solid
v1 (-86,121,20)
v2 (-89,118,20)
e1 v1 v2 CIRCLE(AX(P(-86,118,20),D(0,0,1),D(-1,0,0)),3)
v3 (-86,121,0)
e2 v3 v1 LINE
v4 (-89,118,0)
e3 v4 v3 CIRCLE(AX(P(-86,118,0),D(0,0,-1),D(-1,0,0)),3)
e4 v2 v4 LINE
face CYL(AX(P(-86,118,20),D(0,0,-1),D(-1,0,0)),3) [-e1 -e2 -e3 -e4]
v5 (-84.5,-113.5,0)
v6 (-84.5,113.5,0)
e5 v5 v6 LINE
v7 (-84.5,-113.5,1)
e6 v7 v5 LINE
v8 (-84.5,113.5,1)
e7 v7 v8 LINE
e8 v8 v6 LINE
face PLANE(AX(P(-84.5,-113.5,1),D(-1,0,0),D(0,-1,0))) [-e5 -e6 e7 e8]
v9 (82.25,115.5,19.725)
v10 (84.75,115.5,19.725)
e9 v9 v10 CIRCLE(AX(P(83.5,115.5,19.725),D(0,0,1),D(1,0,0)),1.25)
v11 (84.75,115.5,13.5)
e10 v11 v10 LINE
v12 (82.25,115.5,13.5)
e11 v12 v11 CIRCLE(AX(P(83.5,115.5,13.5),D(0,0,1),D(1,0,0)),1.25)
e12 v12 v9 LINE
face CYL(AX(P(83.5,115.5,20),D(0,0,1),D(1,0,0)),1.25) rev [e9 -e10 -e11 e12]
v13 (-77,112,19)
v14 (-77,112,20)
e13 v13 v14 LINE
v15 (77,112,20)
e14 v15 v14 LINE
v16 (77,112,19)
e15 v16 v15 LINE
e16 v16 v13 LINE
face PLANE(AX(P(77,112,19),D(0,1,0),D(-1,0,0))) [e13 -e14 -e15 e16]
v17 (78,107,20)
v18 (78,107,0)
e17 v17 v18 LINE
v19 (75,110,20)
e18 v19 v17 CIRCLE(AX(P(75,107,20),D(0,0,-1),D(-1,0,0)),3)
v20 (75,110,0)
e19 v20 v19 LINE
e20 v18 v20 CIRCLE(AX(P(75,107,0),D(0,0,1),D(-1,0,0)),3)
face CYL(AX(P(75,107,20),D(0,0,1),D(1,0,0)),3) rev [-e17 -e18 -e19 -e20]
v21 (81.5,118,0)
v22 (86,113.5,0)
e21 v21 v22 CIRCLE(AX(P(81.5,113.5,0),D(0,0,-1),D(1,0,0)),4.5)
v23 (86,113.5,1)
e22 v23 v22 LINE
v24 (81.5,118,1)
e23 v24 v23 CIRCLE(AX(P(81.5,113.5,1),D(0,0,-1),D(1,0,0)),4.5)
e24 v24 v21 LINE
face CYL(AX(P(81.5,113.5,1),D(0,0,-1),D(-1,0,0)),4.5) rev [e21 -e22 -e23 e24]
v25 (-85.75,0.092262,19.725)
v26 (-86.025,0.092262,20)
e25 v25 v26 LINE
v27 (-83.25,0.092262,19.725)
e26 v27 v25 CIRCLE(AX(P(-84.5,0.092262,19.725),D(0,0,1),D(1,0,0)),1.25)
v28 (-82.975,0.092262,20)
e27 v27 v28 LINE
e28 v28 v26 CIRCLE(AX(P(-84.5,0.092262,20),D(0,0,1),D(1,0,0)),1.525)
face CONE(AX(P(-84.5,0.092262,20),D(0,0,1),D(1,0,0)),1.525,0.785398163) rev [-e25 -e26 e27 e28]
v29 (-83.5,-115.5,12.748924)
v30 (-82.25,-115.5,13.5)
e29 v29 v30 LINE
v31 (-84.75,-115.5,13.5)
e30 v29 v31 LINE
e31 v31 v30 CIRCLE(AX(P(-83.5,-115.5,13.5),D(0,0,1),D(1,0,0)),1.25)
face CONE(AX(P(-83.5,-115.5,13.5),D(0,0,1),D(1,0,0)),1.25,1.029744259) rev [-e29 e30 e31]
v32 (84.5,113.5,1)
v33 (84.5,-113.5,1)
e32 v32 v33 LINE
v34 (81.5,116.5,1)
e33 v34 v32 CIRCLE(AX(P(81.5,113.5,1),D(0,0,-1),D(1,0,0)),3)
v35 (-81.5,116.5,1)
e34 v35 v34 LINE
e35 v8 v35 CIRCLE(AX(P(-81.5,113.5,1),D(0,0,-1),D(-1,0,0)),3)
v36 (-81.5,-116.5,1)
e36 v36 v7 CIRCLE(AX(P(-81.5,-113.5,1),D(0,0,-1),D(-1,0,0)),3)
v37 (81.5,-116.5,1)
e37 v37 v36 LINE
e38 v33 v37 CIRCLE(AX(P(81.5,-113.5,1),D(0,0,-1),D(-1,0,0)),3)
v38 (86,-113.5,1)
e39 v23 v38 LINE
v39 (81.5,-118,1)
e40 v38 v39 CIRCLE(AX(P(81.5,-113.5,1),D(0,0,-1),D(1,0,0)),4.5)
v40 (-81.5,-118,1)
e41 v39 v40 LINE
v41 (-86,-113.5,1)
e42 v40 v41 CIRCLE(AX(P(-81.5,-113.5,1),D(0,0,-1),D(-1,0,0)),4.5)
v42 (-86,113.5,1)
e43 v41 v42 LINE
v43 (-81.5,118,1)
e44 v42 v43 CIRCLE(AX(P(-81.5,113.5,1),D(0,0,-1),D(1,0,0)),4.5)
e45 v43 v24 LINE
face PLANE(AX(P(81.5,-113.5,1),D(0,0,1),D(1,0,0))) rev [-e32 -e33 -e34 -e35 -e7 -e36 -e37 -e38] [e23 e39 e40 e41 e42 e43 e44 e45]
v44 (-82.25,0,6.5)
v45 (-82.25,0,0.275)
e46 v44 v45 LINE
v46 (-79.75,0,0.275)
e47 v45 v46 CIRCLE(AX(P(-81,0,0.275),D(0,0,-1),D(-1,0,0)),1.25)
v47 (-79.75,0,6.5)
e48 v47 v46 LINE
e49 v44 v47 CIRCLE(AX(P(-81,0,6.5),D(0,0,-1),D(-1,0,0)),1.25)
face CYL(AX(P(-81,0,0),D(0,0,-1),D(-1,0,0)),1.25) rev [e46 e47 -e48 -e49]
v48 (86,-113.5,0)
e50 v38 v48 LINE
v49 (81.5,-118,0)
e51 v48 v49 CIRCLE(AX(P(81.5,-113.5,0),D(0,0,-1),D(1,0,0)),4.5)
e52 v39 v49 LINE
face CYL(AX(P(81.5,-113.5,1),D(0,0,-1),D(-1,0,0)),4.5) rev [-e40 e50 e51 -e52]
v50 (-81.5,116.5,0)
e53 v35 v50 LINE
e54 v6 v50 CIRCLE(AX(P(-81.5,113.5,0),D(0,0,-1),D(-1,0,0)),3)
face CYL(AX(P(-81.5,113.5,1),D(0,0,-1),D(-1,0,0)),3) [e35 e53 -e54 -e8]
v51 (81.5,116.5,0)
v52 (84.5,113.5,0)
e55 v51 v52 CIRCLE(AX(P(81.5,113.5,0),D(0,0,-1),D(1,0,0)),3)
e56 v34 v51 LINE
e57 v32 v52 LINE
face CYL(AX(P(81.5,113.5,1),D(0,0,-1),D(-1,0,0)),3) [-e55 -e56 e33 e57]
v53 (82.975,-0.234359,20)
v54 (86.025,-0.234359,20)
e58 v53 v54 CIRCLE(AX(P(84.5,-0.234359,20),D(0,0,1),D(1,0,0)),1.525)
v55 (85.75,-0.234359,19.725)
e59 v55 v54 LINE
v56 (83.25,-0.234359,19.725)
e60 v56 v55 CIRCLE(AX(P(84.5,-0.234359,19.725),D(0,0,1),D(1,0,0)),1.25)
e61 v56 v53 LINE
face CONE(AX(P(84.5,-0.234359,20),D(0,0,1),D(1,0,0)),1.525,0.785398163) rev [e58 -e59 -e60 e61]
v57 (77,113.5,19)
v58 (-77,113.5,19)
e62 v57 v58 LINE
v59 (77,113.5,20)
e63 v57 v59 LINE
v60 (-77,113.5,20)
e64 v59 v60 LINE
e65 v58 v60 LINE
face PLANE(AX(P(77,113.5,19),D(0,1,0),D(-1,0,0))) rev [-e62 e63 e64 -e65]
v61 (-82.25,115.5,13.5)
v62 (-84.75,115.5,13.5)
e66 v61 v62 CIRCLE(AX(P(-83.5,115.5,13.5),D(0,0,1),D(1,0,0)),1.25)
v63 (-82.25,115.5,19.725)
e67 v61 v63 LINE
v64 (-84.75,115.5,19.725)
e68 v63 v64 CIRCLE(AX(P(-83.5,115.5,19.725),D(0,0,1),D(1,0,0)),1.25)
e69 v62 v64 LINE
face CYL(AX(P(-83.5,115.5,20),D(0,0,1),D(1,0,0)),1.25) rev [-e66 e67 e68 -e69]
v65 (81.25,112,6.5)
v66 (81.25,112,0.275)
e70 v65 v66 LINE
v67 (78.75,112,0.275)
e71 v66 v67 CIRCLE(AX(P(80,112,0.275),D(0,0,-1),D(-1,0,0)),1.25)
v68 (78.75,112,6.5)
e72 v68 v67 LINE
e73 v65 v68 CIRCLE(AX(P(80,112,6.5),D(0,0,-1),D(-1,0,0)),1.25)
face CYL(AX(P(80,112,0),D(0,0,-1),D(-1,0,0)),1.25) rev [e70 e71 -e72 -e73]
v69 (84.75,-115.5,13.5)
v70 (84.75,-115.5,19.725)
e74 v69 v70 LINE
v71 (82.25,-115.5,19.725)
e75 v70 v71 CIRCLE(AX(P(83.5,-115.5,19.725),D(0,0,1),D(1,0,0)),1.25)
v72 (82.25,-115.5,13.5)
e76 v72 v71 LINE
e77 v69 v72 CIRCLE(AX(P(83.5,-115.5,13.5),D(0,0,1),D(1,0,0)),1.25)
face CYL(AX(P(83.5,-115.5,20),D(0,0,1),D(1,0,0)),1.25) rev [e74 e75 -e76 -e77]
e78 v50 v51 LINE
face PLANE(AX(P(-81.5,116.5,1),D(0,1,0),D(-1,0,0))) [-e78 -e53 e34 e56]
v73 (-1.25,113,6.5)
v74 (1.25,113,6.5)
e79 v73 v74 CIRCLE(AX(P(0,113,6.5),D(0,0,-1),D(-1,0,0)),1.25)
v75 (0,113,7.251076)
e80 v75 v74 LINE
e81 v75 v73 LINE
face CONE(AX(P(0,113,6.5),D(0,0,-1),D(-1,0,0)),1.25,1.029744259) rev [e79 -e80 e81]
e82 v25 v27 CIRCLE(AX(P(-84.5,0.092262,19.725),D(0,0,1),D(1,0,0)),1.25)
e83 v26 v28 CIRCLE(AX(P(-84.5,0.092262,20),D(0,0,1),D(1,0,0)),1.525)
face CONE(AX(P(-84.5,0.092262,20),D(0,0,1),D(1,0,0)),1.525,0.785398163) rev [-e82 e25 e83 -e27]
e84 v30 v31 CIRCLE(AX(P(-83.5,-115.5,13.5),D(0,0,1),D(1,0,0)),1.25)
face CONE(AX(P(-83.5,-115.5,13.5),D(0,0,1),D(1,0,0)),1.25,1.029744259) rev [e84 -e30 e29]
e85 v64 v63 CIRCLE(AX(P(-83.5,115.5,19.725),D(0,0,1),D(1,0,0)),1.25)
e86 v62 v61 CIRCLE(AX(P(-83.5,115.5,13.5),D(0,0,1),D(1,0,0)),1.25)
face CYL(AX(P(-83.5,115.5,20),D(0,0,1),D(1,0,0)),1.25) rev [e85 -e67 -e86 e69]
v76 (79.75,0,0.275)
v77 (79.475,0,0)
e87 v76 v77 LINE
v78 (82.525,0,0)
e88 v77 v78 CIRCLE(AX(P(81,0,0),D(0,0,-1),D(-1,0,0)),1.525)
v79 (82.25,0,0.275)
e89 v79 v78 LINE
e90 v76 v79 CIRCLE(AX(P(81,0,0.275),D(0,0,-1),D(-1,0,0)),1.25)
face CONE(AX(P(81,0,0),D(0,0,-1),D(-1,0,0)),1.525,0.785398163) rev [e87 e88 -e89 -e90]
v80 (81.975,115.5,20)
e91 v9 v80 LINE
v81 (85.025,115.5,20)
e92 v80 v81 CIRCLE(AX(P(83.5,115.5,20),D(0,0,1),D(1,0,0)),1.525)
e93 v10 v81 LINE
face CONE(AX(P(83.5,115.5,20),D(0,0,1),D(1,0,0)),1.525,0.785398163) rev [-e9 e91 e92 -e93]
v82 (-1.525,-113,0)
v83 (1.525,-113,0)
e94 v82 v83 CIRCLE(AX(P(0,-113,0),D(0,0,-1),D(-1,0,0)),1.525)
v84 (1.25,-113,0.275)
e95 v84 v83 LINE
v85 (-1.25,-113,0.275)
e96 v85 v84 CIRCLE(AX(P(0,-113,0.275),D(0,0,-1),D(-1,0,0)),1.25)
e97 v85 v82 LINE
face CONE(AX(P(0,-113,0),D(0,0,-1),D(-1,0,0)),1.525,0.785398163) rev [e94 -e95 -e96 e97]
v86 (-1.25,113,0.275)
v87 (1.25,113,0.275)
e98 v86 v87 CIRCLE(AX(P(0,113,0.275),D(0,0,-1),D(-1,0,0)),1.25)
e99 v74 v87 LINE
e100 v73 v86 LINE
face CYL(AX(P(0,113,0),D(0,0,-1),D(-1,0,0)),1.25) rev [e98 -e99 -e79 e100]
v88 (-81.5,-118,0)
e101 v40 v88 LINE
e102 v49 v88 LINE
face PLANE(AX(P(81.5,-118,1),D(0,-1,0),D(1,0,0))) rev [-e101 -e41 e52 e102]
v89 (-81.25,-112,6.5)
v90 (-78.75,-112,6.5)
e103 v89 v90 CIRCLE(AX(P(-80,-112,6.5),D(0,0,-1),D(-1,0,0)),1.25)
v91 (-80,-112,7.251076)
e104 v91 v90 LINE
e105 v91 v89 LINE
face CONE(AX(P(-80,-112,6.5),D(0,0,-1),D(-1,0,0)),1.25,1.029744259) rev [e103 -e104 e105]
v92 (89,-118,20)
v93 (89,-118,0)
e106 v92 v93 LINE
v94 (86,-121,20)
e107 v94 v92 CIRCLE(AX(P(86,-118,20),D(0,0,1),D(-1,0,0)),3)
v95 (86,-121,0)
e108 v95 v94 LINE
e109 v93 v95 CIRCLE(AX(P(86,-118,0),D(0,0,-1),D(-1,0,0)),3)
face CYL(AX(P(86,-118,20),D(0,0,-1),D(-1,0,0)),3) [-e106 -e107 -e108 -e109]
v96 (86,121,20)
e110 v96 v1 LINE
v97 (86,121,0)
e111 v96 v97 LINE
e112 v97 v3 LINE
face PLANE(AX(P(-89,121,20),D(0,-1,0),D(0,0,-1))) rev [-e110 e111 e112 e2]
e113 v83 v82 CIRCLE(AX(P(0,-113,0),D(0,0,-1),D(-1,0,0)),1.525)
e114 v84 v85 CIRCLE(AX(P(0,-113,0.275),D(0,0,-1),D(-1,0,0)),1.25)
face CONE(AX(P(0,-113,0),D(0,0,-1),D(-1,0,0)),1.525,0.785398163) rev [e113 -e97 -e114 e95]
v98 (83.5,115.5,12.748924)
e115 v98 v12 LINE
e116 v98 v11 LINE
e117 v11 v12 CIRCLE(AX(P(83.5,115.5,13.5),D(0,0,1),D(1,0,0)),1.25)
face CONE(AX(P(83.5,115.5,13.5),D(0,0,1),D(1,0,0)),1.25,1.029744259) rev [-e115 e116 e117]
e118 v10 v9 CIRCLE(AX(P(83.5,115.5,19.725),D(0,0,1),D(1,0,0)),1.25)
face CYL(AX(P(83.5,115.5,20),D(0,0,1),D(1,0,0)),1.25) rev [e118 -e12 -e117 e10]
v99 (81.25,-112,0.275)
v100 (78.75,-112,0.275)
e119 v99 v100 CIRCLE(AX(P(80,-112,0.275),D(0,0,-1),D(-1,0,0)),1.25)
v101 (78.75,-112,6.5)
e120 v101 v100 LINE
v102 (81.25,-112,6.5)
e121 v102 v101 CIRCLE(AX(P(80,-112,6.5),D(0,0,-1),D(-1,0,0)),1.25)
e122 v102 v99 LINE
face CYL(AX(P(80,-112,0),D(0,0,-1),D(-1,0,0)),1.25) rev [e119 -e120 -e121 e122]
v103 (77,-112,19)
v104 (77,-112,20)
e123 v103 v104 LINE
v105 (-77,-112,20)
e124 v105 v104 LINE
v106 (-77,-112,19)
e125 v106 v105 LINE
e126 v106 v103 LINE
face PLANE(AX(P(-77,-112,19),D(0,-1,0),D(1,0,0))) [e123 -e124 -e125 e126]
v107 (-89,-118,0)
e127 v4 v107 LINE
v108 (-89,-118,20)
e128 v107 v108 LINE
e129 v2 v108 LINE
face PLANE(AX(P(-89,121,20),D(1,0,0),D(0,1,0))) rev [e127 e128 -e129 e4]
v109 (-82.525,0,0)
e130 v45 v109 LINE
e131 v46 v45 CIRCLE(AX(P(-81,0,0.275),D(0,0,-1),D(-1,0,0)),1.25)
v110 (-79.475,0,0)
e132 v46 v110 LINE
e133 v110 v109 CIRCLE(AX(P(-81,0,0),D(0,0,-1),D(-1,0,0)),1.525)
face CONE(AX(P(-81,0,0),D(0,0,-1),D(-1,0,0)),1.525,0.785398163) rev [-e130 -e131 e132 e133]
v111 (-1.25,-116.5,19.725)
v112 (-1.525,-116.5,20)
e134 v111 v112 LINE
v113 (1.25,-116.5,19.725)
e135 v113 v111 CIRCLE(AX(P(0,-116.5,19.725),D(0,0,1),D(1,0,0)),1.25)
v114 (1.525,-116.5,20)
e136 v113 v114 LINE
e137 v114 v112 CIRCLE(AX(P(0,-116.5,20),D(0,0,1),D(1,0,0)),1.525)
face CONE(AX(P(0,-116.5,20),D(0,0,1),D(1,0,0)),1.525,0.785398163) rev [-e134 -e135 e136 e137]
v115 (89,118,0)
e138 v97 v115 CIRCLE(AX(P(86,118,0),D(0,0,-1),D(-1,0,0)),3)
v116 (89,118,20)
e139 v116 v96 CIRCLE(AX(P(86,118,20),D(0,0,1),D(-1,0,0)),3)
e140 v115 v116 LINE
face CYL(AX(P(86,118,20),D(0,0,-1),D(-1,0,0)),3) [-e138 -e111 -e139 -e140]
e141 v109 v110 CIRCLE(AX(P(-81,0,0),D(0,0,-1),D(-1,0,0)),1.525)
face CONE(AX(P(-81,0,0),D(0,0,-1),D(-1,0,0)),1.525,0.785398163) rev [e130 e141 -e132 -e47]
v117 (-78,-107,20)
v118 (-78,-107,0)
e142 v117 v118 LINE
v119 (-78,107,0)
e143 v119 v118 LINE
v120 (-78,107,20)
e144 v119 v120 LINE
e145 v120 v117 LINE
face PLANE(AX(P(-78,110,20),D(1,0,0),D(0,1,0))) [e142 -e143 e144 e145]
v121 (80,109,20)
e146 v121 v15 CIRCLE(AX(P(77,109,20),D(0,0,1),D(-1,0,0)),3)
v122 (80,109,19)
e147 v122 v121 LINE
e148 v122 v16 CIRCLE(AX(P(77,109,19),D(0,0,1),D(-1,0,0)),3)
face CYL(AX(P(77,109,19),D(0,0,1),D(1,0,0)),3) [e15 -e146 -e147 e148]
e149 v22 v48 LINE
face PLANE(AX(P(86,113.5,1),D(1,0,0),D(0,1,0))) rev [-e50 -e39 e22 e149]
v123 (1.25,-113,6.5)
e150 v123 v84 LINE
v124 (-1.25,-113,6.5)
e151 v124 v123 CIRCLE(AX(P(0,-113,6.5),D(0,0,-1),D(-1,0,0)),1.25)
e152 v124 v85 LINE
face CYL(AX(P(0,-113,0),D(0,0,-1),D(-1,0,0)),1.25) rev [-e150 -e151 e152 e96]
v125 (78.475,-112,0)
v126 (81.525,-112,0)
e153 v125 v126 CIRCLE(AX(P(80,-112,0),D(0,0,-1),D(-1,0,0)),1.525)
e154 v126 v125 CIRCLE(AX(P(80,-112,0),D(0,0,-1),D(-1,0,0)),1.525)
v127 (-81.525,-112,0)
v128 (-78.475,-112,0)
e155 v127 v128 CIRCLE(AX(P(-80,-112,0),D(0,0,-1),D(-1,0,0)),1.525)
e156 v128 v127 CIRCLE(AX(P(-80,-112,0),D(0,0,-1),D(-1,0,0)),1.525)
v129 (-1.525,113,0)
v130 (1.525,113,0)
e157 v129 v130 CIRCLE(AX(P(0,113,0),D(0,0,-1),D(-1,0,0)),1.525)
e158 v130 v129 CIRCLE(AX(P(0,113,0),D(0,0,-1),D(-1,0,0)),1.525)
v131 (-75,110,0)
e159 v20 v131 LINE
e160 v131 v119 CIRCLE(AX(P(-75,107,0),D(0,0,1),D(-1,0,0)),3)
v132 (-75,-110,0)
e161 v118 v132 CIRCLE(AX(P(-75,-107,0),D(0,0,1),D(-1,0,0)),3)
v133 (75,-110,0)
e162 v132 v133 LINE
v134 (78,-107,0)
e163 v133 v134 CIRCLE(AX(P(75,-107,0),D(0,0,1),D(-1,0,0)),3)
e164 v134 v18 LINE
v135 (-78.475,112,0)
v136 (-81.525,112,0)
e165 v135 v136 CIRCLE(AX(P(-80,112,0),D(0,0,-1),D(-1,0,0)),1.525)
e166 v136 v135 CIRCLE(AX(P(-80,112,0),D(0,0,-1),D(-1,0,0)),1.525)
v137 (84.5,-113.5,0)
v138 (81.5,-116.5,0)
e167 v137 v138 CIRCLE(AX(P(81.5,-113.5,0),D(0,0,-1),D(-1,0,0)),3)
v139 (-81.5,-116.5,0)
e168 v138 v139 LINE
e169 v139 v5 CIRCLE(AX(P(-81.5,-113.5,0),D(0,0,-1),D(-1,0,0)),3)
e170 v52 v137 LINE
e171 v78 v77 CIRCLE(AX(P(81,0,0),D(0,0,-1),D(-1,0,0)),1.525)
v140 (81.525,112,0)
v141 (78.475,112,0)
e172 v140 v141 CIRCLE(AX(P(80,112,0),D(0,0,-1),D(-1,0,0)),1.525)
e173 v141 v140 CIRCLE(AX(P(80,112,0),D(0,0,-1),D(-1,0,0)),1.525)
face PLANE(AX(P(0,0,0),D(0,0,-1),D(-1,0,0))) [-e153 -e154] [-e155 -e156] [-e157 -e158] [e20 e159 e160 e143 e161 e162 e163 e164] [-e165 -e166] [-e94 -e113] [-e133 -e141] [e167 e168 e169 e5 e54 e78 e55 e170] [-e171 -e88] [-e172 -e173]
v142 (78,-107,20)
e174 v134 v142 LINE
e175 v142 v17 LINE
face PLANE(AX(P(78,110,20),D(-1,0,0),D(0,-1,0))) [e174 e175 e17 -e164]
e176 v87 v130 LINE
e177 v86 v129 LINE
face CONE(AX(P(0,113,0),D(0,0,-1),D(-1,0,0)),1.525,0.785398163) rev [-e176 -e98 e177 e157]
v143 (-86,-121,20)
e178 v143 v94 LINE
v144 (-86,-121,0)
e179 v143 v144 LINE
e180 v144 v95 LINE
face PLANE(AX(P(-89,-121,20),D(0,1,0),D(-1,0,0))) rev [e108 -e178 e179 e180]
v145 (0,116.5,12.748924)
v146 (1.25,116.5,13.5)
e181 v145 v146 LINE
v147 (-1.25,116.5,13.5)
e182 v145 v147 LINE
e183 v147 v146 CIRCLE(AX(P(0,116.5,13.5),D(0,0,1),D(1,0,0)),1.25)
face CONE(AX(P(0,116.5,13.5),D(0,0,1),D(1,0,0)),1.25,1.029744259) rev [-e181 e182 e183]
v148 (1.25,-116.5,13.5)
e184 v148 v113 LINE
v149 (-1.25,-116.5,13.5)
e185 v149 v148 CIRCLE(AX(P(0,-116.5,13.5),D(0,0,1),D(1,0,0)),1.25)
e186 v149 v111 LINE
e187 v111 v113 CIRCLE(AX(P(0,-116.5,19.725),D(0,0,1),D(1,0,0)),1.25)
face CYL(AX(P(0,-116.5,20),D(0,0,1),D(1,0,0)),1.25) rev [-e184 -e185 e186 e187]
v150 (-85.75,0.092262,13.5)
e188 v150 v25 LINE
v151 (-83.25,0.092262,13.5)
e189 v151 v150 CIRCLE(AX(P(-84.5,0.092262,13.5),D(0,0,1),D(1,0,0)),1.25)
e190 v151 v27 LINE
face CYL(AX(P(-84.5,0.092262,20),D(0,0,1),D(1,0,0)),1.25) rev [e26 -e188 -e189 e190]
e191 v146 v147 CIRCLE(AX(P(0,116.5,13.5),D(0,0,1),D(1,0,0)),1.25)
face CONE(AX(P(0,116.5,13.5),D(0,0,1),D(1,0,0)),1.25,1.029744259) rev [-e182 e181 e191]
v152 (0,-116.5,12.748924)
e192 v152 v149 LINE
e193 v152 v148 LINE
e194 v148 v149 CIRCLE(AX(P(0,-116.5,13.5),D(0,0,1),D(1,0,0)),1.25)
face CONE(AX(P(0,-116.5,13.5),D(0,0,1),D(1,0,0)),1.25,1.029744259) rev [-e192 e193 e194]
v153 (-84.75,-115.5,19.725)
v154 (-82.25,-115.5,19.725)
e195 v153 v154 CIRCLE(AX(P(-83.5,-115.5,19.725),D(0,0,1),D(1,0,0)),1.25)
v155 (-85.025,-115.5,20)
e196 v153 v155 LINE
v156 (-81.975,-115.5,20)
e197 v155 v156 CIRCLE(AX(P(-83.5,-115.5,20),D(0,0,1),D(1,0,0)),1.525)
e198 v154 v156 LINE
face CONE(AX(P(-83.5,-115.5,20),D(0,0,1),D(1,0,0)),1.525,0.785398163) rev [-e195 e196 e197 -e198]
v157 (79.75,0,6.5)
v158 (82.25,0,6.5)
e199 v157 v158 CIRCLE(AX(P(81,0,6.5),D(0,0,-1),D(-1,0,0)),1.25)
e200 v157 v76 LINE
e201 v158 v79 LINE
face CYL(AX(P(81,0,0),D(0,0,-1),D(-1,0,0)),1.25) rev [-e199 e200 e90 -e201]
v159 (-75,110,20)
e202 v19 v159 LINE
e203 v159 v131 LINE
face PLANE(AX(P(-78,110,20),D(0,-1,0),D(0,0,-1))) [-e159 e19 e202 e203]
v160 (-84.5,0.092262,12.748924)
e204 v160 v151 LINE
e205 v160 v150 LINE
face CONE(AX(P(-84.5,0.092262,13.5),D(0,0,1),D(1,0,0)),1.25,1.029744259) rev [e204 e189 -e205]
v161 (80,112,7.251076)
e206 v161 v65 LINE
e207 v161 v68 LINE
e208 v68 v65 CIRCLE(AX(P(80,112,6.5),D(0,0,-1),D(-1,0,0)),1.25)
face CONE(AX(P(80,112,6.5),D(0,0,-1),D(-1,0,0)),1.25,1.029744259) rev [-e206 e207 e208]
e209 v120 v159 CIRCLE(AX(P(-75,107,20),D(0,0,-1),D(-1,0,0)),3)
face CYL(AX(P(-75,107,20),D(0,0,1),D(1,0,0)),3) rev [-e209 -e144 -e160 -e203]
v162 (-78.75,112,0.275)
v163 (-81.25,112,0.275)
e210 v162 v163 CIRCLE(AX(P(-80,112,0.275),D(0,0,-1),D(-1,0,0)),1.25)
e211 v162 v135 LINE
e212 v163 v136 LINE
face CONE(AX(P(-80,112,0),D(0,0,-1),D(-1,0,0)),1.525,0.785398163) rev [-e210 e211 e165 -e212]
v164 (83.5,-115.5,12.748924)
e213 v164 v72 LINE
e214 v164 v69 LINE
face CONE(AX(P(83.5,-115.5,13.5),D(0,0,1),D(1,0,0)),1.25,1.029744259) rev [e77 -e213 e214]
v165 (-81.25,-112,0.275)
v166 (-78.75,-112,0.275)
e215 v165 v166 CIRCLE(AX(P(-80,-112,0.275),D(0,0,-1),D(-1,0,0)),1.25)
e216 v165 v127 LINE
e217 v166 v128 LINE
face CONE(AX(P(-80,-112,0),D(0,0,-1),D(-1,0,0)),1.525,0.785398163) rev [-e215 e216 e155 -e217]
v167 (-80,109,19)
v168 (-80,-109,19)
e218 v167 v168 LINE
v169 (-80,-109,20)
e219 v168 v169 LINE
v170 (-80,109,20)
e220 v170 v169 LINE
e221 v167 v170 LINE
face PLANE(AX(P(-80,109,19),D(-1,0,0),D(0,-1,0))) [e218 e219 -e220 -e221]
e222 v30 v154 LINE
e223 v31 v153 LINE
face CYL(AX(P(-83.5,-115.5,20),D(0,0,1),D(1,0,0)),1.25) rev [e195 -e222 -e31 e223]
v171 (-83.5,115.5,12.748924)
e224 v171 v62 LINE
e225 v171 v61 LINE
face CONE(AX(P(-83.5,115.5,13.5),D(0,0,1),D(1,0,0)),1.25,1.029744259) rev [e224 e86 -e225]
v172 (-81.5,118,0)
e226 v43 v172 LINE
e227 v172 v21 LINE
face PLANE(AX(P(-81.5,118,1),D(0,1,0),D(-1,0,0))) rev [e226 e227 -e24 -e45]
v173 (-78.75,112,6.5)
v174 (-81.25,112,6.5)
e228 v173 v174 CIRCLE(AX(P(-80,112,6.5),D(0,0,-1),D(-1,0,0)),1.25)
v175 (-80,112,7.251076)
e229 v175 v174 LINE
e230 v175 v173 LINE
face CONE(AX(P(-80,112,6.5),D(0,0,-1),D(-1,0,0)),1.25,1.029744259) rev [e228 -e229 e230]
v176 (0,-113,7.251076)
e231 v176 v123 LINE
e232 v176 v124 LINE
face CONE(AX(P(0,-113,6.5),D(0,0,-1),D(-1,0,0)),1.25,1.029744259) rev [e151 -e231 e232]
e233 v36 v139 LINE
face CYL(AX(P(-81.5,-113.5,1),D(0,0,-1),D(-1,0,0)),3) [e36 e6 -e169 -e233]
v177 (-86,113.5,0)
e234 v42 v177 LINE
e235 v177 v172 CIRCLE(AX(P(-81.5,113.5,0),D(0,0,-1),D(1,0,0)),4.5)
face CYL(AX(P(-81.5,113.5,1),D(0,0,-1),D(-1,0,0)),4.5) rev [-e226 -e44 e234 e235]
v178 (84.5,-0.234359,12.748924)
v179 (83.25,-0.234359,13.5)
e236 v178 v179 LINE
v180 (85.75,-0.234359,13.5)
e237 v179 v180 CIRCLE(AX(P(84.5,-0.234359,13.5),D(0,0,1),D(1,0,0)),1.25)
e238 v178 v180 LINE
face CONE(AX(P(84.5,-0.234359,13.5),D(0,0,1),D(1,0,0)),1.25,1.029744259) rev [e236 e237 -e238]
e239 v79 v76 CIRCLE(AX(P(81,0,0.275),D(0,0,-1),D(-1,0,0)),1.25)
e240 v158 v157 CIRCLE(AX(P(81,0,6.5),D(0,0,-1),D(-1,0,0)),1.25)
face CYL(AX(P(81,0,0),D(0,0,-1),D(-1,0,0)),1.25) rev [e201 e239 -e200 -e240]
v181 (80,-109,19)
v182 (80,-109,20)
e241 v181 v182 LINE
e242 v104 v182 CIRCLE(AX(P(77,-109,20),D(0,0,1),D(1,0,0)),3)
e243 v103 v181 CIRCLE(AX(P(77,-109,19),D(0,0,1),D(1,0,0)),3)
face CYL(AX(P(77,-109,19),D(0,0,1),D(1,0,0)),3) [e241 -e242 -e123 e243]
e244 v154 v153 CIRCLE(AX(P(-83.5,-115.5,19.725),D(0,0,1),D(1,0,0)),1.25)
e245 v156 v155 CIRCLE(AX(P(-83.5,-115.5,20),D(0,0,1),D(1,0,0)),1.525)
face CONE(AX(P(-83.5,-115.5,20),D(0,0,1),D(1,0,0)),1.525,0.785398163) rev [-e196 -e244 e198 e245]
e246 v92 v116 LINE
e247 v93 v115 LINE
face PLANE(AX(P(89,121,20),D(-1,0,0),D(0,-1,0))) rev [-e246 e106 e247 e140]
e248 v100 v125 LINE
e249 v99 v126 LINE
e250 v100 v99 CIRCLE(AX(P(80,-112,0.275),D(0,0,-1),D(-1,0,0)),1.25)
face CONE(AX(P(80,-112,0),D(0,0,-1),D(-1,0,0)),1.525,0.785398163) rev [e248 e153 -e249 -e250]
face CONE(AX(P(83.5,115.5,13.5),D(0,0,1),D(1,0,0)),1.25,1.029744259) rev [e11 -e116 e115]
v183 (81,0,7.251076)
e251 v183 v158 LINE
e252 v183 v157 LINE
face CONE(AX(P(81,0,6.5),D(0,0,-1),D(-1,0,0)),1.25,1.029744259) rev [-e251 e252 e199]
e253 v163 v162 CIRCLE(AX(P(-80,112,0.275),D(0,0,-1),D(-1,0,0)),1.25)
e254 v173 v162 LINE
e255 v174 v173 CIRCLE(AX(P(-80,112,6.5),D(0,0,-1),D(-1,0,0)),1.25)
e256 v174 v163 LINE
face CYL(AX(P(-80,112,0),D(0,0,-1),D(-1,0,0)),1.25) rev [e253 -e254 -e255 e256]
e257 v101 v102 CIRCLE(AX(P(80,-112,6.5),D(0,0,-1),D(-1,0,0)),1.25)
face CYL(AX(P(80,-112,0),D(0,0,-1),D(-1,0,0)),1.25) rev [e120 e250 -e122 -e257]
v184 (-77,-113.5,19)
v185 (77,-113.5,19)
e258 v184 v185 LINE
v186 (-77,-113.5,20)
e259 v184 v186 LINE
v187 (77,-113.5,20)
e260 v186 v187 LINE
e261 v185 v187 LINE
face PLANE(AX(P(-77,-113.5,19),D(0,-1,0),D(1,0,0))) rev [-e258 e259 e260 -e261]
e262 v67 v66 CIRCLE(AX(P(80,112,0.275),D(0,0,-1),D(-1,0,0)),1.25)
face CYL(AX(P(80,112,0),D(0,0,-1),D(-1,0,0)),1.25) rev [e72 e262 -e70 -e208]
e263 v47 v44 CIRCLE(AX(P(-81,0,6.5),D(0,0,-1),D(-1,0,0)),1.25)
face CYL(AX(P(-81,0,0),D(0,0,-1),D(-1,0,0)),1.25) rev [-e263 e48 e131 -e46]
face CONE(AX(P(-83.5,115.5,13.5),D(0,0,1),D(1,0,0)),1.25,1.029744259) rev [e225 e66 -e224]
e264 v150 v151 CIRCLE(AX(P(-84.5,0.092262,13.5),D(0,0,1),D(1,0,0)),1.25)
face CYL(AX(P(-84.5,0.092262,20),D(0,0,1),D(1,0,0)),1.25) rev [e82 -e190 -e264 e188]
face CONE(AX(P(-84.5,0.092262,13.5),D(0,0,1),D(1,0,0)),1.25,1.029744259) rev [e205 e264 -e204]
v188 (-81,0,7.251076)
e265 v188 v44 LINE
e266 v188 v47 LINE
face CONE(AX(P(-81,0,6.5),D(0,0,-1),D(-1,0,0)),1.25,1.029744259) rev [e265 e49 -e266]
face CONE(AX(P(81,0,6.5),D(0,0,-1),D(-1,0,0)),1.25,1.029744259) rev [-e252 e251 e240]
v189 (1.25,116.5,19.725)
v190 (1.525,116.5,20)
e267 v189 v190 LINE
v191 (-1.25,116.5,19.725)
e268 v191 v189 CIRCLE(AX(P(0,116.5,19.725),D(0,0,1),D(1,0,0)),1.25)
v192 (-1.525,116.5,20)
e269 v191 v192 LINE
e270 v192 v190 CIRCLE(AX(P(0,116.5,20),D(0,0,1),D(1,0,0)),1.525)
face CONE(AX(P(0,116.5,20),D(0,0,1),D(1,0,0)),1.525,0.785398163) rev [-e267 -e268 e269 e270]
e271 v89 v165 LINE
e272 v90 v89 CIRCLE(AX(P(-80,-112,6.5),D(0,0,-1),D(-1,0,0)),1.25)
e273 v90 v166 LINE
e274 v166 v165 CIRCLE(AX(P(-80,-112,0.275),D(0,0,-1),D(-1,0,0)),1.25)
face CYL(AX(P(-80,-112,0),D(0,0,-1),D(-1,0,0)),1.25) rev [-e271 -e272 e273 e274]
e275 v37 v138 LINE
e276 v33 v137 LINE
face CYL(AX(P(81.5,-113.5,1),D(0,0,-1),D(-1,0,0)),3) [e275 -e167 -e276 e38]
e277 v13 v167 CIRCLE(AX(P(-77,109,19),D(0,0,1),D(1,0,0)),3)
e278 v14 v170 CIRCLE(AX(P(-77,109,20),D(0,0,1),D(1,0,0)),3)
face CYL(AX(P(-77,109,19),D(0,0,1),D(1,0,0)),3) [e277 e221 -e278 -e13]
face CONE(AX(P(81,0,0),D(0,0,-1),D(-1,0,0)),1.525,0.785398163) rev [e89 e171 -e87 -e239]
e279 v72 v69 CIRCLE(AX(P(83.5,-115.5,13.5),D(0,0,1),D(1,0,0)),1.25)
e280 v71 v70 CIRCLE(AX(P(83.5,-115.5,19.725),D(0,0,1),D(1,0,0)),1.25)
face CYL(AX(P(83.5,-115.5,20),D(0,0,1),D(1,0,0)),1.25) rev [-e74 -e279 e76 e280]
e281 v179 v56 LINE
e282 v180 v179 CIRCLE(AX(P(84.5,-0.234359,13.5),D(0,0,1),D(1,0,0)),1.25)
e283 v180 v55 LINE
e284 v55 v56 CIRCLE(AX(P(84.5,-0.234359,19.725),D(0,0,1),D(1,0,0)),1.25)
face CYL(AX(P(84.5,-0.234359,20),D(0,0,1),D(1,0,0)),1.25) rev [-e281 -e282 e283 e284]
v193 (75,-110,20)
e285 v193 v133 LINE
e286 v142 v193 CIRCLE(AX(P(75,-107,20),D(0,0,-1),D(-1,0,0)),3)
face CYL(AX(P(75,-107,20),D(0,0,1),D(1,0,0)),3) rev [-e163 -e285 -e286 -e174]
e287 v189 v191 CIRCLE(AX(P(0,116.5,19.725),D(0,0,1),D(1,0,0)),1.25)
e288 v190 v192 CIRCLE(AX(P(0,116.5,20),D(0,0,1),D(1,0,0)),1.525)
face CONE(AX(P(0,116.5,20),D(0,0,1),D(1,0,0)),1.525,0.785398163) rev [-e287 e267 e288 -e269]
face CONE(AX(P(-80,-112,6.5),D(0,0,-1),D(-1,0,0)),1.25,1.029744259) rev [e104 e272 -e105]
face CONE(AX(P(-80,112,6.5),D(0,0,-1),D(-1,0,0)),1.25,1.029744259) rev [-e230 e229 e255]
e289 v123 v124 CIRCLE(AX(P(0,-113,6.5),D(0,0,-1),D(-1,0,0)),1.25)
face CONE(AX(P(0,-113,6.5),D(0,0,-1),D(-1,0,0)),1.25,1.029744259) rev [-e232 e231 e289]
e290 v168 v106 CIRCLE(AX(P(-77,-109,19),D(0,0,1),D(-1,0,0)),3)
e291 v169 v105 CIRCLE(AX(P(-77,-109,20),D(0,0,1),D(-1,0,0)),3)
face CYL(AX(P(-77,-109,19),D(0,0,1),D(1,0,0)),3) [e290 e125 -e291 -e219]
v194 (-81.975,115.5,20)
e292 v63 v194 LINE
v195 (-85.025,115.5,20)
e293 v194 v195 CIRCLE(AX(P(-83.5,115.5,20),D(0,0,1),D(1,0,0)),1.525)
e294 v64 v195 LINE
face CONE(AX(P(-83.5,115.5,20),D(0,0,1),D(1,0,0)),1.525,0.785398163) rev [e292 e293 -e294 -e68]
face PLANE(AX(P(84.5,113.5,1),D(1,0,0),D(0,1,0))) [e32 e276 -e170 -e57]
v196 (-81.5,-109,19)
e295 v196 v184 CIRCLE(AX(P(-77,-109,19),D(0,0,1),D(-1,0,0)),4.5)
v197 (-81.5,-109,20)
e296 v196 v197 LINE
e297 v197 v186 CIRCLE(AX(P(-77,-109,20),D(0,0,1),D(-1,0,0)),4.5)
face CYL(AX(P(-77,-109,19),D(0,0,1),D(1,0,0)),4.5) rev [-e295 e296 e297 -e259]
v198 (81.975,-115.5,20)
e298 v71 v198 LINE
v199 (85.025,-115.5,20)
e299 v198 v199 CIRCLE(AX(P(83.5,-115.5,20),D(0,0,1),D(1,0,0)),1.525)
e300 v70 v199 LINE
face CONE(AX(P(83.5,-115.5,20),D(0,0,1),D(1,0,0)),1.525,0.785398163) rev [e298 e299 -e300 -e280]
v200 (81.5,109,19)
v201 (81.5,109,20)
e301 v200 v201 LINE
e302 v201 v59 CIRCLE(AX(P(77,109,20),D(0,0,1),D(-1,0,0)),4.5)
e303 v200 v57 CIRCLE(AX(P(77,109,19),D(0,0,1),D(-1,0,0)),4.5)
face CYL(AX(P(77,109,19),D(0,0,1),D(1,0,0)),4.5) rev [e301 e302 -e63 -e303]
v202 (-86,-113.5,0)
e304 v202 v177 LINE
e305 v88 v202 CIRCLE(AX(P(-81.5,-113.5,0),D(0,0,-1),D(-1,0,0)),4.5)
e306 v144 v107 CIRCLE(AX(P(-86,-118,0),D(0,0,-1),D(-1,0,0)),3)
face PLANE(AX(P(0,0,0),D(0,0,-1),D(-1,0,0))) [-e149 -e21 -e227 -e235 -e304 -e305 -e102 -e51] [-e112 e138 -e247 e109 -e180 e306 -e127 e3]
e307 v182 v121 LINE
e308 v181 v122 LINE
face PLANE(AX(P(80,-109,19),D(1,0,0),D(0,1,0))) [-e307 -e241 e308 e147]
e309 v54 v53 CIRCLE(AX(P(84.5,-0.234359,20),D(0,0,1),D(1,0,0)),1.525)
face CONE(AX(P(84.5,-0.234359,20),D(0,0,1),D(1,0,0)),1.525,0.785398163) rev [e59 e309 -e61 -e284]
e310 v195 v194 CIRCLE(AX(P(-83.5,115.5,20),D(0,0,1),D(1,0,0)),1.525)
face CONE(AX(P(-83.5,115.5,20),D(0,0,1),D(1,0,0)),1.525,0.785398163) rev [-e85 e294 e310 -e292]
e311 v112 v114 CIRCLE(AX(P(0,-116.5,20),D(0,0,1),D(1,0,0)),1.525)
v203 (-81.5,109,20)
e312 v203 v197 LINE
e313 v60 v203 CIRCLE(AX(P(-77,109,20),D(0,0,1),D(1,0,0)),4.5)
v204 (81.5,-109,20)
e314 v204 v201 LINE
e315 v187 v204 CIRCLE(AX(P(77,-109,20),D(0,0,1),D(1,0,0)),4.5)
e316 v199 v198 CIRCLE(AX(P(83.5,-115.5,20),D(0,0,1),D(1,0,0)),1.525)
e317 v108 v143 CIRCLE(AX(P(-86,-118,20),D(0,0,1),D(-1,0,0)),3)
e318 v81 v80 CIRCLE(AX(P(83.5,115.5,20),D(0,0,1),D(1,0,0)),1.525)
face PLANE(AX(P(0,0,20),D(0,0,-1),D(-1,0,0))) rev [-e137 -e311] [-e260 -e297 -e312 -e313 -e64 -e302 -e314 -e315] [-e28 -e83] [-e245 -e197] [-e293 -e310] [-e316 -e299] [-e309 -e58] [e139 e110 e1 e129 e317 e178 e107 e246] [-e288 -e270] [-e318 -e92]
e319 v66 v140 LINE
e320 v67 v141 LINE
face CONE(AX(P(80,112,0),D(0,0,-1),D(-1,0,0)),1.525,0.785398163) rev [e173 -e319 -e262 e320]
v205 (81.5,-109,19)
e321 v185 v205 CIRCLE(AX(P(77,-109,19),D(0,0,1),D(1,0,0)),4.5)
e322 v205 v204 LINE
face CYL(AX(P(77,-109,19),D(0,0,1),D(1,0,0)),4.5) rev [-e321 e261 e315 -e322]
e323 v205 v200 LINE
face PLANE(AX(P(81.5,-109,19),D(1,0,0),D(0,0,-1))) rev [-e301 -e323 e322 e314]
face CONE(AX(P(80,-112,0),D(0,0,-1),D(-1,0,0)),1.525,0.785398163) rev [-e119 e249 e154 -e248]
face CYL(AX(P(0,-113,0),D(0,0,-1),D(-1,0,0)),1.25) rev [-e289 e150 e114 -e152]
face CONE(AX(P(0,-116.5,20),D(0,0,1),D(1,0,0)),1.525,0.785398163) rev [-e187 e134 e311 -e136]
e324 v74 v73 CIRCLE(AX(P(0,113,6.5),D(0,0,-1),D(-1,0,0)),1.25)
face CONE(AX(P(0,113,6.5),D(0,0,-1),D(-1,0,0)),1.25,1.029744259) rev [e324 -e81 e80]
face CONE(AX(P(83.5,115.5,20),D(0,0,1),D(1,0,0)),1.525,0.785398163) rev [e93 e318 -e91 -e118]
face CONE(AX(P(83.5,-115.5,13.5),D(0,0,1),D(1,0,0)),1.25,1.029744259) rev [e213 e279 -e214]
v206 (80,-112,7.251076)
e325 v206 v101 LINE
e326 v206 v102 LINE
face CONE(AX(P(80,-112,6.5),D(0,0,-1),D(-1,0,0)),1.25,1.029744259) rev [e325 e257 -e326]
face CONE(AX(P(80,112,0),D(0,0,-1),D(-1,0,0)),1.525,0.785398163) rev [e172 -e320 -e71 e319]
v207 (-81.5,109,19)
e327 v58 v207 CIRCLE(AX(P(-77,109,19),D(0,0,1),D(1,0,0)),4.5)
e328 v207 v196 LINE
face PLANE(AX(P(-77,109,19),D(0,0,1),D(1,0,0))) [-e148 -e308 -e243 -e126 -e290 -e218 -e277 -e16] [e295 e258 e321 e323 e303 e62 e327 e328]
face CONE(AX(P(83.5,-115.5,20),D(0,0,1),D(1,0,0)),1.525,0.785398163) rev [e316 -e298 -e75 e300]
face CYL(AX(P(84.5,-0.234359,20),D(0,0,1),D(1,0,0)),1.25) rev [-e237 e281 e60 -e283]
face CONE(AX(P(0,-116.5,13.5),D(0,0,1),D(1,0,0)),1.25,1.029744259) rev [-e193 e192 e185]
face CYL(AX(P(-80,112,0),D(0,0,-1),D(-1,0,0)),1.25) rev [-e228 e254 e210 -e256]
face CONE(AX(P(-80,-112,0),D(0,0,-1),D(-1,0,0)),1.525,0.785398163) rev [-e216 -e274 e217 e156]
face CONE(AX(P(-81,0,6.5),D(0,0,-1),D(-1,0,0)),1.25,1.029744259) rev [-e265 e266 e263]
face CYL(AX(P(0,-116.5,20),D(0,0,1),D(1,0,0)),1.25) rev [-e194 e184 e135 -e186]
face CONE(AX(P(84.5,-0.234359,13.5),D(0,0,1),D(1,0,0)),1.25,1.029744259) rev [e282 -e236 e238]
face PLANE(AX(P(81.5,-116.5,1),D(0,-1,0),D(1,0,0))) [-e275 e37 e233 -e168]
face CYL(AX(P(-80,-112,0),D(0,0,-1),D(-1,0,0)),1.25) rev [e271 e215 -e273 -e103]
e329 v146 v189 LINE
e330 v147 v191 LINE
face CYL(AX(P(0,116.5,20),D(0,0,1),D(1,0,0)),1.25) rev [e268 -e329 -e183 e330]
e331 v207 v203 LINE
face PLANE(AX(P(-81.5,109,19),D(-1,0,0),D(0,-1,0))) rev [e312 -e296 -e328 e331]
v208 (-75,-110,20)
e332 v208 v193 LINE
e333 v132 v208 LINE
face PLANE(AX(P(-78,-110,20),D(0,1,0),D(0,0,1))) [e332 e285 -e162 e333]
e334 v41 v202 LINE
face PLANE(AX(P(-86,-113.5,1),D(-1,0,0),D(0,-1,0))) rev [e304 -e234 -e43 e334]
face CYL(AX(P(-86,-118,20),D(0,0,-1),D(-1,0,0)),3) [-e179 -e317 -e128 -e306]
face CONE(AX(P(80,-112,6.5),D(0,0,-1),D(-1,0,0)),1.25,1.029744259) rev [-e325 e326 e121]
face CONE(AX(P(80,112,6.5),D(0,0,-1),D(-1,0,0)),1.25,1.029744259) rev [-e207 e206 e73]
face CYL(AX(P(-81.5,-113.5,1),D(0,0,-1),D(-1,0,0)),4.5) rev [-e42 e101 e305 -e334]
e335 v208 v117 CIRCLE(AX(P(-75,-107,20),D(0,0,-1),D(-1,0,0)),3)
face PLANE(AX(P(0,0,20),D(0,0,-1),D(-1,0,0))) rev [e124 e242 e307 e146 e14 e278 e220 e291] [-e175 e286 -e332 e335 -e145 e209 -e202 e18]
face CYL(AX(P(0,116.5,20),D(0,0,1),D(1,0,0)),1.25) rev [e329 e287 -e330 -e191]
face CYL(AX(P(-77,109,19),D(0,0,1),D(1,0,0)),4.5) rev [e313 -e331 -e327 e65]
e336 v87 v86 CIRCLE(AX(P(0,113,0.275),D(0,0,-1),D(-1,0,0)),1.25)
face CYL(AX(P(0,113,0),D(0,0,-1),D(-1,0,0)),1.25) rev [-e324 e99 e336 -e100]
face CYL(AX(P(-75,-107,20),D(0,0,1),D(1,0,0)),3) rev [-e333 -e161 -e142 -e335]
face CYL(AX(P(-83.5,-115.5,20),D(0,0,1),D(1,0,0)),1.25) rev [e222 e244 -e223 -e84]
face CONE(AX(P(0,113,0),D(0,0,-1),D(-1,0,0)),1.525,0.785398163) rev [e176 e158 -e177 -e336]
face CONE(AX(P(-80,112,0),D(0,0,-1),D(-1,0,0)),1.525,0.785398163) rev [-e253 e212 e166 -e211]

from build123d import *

# Parameters (mm, degrees)
SKETCH1_W                   = 178
SKETCH1_H                   = 242
SKETCH1_W_2                 = 156
SKETCH1_H_2                 = 220
BOSS_EXTRUDE1_DEPTH         = 20
FILLET1_R                   = 3
CUT_EXTRUDE1_DEPTH          = 1
M3_TAPPED_HOLE2_D           = 2.5
M3_TAPPED_HOLE2_DEPTH       = 6.5
M3_TAPPED_HOLE2_CSINK_D     = 3.05
M3_TAPPED_HOLE2_CSINK_ANGLE = 90
M3_TAPPED_HOLE2_TIP         = 0.751075774
M3_TAPPED_HOLE1_D           = 2.5
M3_TAPPED_HOLE1_DEPTH       = 6.5
M3_TAPPED_HOLE1_CSINK_D     = 3.05
M3_TAPPED_HOLE1_CSINK_ANGLE = 90
M3_TAPPED_HOLE1_TIP         = 0.751075774
CUT_EXTRUDE2_DEPTH          = 1


with BuildPart() as part:
    # Sketch1 → Boss-Extrude1 (new body)
    with BuildSketch(Plane.XY):
        Rectangle(SKETCH1_W, SKETCH1_H)
        Rectangle(SKETCH1_W_2, SKETCH1_H_2, mode=Mode.SUBTRACT)
    extrude(amount=BOSS_EXTRUDE1_DEPTH)

    # Fillet1
    fillet1_edges = [part.edges().sort_by_distance(p)[0] for p in [
        (78, -110, 10),
        (78, 110, 10),
        (-78, 110, 10),
        (-78, -110, 10),
        (89, 121, 10),
        (89, -121, 10),
        (-89, -121, 10),
        (-89, 121, 10),
    ]]
    fillet(fillet1_edges, radius=FILLET1_R)

    # Sketch2 → Cut-Extrude1 (cut)
    with BuildSketch(Plane.XY.offset(20)):
        with BuildLine():
            Line((-81.5, 109), (-81.5, -109))
            ThreePointArc((-81.5, -109), (-80.181980515, -112.181980515), (-77, -113.5))
            Line((-77, -113.5), (77, -113.5))
            ThreePointArc((77, -113.5), (80.181980515, -112.181980515), (81.5, -109))
            Line((81.5, -109), (81.5, 109))
            ThreePointArc((81.5, 109), (80.181980515, 112.181980515), (77, 113.5))
            Line((77, 113.5), (-77, 113.5))
            ThreePointArc((-77, 113.5), (-80.181980515, 112.181980515), (-81.5, 109))
        make_face()
        with BuildLine():
            Line((-77, -112), (77, -112))
            ThreePointArc((77, -112), (79.121320344, -111.121320344), (80, -109))
            Line((80, -109), (80, 109))
            ThreePointArc((80, 109), (79.121320344, 111.121320344), (77, 112))
            Line((77, 112), (-77, 112))
            ThreePointArc((-77, 112), (-79.121320344, 111.121320344), (-80, 109))
            Line((-80, 109), (-80, -109))
            ThreePointArc((-80, -109), (-79.121320344, -111.121320344), (-77, -112))
        make_face(mode=Mode.SUBTRACT)
    extrude(amount=-CUT_EXTRUDE1_DEPTH, mode=Mode.SUBTRACT)

    # M3 Tapped Hole2
    with Locations(Plane.XY.offset(20)):
        with Locations((-83.5, 115.5), (0, 116.5), (83.5, 115.5), (-84.5, 0.09226209), (84.5, -0.23435851), (0, -116.5), (-83.5, -115.5), (83.5, -115.5)):
            CounterSinkHole(M3_TAPPED_HOLE2_D / 2, M3_TAPPED_HOLE2_CSINK_D / 2, depth=M3_TAPPED_HOLE2_DEPTH, counter_sink_angle=M3_TAPPED_HOLE2_CSINK_ANGLE)
            with Locations((0, 0, -(M3_TAPPED_HOLE2_DEPTH + M3_TAPPED_HOLE2_TIP / 2))):  # 118° drill point
                Cone(0, M3_TAPPED_HOLE2_D / 2, M3_TAPPED_HOLE2_TIP, mode=Mode.SUBTRACT)

    # M3 Tapped Hole1
    with Locations(Plane(origin=(0, 0, 0), x_dir=(-1, 0, 0), z_dir=(0, 0, -1))):
        with Locations((0, 113), (-81, 0), (81, 0), (0, -113), (80, -112), (-80, -112), (-80, 112), (80, 112)):
            CounterSinkHole(M3_TAPPED_HOLE1_D / 2, M3_TAPPED_HOLE1_CSINK_D / 2, depth=M3_TAPPED_HOLE1_DEPTH, counter_sink_angle=M3_TAPPED_HOLE1_CSINK_ANGLE)
            with Locations((0, 0, -(M3_TAPPED_HOLE1_DEPTH + M3_TAPPED_HOLE1_TIP / 2))):  # 118° drill point
                Cone(0, M3_TAPPED_HOLE1_D / 2, M3_TAPPED_HOLE1_TIP, mode=Mode.SUBTRACT)

    # Sketch5 → Cut-Extrude2 (cut)
    with BuildSketch(Plane(origin=(0, 0, 0), x_dir=(-1, 0, 0), z_dir=(0, 0, -1))):
        with BuildLine():
            Line((-81.5, -118), (81.5, -118))
            ThreePointArc((81.5, -118), (84.681980515, -116.681980515), (86, -113.5))
            Line((86, -113.5), (86, 113.5))
            ThreePointArc((86, 113.5), (84.681980515, 116.681980515), (81.5, 118))
            Line((81.5, 118), (-81.5, 118))
            ThreePointArc((-81.5, 118), (-84.681980515, 116.681980515), (-86, 113.5))
            Line((-86, 113.5), (-86, -113.5))
            ThreePointArc((-86, -113.5), (-84.681980515, -116.681980515), (-81.5, -118))
        make_face()
        with BuildLine():
            Line((-84.5, 113.5), (-84.5, -113.5))
            ThreePointArc((-84.5, -113.5), (-83.621320344, -115.621320344), (-81.5, -116.5))
            Line((-81.5, -116.5), (81.5, -116.5))
            ThreePointArc((81.5, -116.5), (83.621320344, -115.621320344), (84.5, -113.5))
            Line((84.5, -113.5), (84.5, 113.5))
            ThreePointArc((84.5, 113.5), (83.621320344, 115.621320344), (81.5, 116.5))
            Line((81.5, 116.5), (-81.5, 116.5))
            ThreePointArc((-81.5, 116.5), (-83.621320344, 115.621320344), (-84.5, 113.5))
        make_face(mode=Mode.SUBTRACT)
    extrude(amount=-CUT_EXTRUDE2_DEPTH, mode=Mode.SUBTRACT)


solid = part.part
